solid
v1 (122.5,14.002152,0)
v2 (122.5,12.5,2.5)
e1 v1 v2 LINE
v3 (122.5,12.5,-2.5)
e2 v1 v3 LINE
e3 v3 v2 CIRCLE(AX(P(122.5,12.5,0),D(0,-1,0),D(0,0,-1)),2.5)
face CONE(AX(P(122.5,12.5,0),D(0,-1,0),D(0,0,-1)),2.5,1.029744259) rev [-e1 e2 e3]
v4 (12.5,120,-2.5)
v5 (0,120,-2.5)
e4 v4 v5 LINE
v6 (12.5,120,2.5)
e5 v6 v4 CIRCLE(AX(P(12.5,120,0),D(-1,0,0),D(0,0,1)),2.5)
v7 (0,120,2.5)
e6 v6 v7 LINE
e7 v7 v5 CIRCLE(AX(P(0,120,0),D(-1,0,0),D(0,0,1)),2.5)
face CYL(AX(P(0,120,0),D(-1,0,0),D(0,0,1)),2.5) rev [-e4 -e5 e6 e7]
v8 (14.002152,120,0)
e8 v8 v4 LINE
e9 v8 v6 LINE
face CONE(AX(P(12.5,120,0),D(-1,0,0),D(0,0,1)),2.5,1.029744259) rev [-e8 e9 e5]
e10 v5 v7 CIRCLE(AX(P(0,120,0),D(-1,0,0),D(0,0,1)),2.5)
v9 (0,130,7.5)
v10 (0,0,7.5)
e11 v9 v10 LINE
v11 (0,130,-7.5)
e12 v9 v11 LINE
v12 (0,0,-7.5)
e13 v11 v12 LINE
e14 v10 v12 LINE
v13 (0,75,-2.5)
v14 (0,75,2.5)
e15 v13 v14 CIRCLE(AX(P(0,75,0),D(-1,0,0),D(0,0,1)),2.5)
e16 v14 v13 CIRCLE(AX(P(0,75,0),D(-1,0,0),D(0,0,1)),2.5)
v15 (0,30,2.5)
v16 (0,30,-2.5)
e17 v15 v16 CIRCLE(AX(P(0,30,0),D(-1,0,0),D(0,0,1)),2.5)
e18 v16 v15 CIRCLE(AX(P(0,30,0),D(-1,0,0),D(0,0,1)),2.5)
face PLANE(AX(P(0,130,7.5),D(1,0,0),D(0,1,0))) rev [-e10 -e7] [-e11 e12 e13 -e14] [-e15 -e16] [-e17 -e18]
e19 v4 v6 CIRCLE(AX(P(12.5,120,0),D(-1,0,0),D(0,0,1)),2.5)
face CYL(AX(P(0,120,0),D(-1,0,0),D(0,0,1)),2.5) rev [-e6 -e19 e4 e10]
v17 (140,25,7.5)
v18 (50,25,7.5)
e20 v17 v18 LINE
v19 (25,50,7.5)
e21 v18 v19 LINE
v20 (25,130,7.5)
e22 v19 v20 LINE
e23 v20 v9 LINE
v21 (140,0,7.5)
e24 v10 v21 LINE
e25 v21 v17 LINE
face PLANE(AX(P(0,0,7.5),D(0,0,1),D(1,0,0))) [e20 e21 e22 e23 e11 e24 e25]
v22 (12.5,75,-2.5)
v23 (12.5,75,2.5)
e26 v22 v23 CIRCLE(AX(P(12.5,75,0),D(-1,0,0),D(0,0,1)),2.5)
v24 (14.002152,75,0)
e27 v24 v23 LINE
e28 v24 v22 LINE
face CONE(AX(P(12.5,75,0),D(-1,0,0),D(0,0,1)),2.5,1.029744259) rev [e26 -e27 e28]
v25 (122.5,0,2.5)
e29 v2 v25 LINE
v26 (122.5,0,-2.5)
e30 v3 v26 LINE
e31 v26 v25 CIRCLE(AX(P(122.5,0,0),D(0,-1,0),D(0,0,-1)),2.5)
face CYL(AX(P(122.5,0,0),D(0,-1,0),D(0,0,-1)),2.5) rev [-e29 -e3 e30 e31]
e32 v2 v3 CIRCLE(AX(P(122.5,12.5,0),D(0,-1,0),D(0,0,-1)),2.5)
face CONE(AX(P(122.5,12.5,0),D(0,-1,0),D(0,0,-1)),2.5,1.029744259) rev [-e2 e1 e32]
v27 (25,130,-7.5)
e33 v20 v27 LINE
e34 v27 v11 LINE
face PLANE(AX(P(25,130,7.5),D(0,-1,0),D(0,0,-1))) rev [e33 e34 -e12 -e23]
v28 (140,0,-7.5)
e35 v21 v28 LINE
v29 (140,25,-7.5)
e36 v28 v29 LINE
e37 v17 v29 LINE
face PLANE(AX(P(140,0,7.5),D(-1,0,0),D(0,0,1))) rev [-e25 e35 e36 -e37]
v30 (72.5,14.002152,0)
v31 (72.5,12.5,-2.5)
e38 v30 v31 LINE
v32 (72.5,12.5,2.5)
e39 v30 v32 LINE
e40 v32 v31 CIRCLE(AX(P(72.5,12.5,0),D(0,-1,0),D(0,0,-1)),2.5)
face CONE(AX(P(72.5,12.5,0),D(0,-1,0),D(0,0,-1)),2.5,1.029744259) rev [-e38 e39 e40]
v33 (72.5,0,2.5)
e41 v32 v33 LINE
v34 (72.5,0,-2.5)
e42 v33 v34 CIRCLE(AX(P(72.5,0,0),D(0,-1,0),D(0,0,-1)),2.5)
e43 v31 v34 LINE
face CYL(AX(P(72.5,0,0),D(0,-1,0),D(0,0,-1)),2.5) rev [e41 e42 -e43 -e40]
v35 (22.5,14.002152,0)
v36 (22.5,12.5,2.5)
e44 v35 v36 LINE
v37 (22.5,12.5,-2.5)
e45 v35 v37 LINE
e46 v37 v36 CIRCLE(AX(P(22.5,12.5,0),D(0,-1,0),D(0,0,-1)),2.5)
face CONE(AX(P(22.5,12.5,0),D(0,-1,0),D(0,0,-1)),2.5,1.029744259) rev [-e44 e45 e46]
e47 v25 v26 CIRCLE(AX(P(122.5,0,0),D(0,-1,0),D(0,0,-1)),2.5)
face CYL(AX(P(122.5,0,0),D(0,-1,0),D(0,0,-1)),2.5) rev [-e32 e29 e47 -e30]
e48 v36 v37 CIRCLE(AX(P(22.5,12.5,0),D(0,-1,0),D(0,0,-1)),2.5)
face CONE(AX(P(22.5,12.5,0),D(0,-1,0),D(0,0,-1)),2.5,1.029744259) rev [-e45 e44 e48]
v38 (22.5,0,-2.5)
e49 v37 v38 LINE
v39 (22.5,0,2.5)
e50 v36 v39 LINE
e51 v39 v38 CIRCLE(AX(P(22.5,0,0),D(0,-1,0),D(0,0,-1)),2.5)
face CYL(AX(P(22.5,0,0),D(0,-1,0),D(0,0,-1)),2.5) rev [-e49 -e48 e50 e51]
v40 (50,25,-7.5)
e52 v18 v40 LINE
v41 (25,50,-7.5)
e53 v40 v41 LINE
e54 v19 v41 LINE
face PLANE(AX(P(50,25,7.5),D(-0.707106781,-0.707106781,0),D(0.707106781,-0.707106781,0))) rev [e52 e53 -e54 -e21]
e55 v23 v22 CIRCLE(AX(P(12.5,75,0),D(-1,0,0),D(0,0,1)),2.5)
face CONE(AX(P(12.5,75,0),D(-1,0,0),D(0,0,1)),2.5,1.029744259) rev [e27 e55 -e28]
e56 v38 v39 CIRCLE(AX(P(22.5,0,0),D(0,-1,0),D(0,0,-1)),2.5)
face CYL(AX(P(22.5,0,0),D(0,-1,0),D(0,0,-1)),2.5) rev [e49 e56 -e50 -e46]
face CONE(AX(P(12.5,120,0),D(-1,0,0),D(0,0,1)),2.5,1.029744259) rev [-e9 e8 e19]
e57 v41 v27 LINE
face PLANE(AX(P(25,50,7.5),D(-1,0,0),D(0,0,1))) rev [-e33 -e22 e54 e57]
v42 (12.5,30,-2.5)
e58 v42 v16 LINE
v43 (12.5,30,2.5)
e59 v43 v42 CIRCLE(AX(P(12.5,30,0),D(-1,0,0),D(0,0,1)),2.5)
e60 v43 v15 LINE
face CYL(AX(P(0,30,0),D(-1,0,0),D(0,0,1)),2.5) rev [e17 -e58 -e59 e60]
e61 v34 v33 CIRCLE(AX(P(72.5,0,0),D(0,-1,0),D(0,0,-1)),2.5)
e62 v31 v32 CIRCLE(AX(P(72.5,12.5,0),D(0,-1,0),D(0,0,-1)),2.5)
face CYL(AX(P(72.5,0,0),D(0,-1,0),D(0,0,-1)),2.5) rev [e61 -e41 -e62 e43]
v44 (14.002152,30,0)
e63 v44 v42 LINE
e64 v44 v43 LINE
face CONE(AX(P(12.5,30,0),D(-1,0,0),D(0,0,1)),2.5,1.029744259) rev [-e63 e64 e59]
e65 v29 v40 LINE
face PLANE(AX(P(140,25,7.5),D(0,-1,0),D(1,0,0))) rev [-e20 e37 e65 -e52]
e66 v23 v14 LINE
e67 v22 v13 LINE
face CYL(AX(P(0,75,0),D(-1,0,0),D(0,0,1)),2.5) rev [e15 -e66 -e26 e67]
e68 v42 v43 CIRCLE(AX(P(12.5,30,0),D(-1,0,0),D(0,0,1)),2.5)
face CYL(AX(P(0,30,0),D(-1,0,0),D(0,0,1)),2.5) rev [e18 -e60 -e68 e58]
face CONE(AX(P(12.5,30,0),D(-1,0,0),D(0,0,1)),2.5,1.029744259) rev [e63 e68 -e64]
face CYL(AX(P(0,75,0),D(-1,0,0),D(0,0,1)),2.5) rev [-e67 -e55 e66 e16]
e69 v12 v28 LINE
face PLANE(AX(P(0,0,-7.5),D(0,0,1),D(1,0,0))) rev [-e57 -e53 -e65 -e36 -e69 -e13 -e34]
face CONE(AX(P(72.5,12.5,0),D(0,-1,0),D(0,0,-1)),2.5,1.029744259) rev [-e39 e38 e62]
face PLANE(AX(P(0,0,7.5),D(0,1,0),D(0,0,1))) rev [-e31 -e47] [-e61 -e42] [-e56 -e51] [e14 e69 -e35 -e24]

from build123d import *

# Parameters (mm, degrees)
EXTRUDE_1_DEPTH                  = 7.5
HOLE_WIZARD_M6_1_D               = 5
HOLE_WIZARD_M6_1_DEPTH           = 12.5
HOLE_WIZARD_M6_1_TIP             = 1.502151548
HOLE_WIZARD_M6_1_ON_FACE_2_D     = 5
HOLE_WIZARD_M6_1_ON_FACE_2_DEPTH = 12.5
HOLE_WIZARD_M6_1_ON_FACE_2_TIP   = 1.502151548


with BuildPart() as part:
    # 草图1 → 凸台-拉伸1 (new, symmetric)
    with BuildSketch(Plane.XY):
        Polygon((0, 130), (0, 0), (140, 0), (140, 25), (50, 25), (25, 50), (25, 130), align=None)
    extrude(amount=EXTRUDE_1_DEPTH, both=True)

    # M6 螺纹孔1
    with Locations(Plane(origin=(122.5, 0, 0), x_dir=(0, 0, -1), z_dir=(0, -1, 0))):
        with Locations((0, 0), (0, -50), (0, -100)):
            Hole(HOLE_WIZARD_M6_1_D / 2, depth=HOLE_WIZARD_M6_1_DEPTH)
            with Locations((0, 0, -(HOLE_WIZARD_M6_1_DEPTH + HOLE_WIZARD_M6_1_TIP / 2))):  # 118° drill point
                Cone(0, HOLE_WIZARD_M6_1_D / 2, HOLE_WIZARD_M6_1_TIP, mode=Mode.SUBTRACT)

    # M6 螺纹孔1 on face 2
    with Locations(Plane(origin=(0, 30, 0), x_dir=(0, 0, -1), z_dir=(-1, 0, 0))):
        with Locations((0, 0), (0, -45), (0, -90)):
            Hole(HOLE_WIZARD_M6_1_ON_FACE_2_D / 2, depth=HOLE_WIZARD_M6_1_ON_FACE_2_DEPTH)
            with Locations((0, 0, -(HOLE_WIZARD_M6_1_ON_FACE_2_DEPTH + HOLE_WIZARD_M6_1_ON_FACE_2_TIP / 2))):  # 118° drill point
                Cone(0, HOLE_WIZARD_M6_1_ON_FACE_2_D / 2, HOLE_WIZARD_M6_1_ON_FACE_2_TIP, mode=Mode.SUBTRACT)


solid = part.part
